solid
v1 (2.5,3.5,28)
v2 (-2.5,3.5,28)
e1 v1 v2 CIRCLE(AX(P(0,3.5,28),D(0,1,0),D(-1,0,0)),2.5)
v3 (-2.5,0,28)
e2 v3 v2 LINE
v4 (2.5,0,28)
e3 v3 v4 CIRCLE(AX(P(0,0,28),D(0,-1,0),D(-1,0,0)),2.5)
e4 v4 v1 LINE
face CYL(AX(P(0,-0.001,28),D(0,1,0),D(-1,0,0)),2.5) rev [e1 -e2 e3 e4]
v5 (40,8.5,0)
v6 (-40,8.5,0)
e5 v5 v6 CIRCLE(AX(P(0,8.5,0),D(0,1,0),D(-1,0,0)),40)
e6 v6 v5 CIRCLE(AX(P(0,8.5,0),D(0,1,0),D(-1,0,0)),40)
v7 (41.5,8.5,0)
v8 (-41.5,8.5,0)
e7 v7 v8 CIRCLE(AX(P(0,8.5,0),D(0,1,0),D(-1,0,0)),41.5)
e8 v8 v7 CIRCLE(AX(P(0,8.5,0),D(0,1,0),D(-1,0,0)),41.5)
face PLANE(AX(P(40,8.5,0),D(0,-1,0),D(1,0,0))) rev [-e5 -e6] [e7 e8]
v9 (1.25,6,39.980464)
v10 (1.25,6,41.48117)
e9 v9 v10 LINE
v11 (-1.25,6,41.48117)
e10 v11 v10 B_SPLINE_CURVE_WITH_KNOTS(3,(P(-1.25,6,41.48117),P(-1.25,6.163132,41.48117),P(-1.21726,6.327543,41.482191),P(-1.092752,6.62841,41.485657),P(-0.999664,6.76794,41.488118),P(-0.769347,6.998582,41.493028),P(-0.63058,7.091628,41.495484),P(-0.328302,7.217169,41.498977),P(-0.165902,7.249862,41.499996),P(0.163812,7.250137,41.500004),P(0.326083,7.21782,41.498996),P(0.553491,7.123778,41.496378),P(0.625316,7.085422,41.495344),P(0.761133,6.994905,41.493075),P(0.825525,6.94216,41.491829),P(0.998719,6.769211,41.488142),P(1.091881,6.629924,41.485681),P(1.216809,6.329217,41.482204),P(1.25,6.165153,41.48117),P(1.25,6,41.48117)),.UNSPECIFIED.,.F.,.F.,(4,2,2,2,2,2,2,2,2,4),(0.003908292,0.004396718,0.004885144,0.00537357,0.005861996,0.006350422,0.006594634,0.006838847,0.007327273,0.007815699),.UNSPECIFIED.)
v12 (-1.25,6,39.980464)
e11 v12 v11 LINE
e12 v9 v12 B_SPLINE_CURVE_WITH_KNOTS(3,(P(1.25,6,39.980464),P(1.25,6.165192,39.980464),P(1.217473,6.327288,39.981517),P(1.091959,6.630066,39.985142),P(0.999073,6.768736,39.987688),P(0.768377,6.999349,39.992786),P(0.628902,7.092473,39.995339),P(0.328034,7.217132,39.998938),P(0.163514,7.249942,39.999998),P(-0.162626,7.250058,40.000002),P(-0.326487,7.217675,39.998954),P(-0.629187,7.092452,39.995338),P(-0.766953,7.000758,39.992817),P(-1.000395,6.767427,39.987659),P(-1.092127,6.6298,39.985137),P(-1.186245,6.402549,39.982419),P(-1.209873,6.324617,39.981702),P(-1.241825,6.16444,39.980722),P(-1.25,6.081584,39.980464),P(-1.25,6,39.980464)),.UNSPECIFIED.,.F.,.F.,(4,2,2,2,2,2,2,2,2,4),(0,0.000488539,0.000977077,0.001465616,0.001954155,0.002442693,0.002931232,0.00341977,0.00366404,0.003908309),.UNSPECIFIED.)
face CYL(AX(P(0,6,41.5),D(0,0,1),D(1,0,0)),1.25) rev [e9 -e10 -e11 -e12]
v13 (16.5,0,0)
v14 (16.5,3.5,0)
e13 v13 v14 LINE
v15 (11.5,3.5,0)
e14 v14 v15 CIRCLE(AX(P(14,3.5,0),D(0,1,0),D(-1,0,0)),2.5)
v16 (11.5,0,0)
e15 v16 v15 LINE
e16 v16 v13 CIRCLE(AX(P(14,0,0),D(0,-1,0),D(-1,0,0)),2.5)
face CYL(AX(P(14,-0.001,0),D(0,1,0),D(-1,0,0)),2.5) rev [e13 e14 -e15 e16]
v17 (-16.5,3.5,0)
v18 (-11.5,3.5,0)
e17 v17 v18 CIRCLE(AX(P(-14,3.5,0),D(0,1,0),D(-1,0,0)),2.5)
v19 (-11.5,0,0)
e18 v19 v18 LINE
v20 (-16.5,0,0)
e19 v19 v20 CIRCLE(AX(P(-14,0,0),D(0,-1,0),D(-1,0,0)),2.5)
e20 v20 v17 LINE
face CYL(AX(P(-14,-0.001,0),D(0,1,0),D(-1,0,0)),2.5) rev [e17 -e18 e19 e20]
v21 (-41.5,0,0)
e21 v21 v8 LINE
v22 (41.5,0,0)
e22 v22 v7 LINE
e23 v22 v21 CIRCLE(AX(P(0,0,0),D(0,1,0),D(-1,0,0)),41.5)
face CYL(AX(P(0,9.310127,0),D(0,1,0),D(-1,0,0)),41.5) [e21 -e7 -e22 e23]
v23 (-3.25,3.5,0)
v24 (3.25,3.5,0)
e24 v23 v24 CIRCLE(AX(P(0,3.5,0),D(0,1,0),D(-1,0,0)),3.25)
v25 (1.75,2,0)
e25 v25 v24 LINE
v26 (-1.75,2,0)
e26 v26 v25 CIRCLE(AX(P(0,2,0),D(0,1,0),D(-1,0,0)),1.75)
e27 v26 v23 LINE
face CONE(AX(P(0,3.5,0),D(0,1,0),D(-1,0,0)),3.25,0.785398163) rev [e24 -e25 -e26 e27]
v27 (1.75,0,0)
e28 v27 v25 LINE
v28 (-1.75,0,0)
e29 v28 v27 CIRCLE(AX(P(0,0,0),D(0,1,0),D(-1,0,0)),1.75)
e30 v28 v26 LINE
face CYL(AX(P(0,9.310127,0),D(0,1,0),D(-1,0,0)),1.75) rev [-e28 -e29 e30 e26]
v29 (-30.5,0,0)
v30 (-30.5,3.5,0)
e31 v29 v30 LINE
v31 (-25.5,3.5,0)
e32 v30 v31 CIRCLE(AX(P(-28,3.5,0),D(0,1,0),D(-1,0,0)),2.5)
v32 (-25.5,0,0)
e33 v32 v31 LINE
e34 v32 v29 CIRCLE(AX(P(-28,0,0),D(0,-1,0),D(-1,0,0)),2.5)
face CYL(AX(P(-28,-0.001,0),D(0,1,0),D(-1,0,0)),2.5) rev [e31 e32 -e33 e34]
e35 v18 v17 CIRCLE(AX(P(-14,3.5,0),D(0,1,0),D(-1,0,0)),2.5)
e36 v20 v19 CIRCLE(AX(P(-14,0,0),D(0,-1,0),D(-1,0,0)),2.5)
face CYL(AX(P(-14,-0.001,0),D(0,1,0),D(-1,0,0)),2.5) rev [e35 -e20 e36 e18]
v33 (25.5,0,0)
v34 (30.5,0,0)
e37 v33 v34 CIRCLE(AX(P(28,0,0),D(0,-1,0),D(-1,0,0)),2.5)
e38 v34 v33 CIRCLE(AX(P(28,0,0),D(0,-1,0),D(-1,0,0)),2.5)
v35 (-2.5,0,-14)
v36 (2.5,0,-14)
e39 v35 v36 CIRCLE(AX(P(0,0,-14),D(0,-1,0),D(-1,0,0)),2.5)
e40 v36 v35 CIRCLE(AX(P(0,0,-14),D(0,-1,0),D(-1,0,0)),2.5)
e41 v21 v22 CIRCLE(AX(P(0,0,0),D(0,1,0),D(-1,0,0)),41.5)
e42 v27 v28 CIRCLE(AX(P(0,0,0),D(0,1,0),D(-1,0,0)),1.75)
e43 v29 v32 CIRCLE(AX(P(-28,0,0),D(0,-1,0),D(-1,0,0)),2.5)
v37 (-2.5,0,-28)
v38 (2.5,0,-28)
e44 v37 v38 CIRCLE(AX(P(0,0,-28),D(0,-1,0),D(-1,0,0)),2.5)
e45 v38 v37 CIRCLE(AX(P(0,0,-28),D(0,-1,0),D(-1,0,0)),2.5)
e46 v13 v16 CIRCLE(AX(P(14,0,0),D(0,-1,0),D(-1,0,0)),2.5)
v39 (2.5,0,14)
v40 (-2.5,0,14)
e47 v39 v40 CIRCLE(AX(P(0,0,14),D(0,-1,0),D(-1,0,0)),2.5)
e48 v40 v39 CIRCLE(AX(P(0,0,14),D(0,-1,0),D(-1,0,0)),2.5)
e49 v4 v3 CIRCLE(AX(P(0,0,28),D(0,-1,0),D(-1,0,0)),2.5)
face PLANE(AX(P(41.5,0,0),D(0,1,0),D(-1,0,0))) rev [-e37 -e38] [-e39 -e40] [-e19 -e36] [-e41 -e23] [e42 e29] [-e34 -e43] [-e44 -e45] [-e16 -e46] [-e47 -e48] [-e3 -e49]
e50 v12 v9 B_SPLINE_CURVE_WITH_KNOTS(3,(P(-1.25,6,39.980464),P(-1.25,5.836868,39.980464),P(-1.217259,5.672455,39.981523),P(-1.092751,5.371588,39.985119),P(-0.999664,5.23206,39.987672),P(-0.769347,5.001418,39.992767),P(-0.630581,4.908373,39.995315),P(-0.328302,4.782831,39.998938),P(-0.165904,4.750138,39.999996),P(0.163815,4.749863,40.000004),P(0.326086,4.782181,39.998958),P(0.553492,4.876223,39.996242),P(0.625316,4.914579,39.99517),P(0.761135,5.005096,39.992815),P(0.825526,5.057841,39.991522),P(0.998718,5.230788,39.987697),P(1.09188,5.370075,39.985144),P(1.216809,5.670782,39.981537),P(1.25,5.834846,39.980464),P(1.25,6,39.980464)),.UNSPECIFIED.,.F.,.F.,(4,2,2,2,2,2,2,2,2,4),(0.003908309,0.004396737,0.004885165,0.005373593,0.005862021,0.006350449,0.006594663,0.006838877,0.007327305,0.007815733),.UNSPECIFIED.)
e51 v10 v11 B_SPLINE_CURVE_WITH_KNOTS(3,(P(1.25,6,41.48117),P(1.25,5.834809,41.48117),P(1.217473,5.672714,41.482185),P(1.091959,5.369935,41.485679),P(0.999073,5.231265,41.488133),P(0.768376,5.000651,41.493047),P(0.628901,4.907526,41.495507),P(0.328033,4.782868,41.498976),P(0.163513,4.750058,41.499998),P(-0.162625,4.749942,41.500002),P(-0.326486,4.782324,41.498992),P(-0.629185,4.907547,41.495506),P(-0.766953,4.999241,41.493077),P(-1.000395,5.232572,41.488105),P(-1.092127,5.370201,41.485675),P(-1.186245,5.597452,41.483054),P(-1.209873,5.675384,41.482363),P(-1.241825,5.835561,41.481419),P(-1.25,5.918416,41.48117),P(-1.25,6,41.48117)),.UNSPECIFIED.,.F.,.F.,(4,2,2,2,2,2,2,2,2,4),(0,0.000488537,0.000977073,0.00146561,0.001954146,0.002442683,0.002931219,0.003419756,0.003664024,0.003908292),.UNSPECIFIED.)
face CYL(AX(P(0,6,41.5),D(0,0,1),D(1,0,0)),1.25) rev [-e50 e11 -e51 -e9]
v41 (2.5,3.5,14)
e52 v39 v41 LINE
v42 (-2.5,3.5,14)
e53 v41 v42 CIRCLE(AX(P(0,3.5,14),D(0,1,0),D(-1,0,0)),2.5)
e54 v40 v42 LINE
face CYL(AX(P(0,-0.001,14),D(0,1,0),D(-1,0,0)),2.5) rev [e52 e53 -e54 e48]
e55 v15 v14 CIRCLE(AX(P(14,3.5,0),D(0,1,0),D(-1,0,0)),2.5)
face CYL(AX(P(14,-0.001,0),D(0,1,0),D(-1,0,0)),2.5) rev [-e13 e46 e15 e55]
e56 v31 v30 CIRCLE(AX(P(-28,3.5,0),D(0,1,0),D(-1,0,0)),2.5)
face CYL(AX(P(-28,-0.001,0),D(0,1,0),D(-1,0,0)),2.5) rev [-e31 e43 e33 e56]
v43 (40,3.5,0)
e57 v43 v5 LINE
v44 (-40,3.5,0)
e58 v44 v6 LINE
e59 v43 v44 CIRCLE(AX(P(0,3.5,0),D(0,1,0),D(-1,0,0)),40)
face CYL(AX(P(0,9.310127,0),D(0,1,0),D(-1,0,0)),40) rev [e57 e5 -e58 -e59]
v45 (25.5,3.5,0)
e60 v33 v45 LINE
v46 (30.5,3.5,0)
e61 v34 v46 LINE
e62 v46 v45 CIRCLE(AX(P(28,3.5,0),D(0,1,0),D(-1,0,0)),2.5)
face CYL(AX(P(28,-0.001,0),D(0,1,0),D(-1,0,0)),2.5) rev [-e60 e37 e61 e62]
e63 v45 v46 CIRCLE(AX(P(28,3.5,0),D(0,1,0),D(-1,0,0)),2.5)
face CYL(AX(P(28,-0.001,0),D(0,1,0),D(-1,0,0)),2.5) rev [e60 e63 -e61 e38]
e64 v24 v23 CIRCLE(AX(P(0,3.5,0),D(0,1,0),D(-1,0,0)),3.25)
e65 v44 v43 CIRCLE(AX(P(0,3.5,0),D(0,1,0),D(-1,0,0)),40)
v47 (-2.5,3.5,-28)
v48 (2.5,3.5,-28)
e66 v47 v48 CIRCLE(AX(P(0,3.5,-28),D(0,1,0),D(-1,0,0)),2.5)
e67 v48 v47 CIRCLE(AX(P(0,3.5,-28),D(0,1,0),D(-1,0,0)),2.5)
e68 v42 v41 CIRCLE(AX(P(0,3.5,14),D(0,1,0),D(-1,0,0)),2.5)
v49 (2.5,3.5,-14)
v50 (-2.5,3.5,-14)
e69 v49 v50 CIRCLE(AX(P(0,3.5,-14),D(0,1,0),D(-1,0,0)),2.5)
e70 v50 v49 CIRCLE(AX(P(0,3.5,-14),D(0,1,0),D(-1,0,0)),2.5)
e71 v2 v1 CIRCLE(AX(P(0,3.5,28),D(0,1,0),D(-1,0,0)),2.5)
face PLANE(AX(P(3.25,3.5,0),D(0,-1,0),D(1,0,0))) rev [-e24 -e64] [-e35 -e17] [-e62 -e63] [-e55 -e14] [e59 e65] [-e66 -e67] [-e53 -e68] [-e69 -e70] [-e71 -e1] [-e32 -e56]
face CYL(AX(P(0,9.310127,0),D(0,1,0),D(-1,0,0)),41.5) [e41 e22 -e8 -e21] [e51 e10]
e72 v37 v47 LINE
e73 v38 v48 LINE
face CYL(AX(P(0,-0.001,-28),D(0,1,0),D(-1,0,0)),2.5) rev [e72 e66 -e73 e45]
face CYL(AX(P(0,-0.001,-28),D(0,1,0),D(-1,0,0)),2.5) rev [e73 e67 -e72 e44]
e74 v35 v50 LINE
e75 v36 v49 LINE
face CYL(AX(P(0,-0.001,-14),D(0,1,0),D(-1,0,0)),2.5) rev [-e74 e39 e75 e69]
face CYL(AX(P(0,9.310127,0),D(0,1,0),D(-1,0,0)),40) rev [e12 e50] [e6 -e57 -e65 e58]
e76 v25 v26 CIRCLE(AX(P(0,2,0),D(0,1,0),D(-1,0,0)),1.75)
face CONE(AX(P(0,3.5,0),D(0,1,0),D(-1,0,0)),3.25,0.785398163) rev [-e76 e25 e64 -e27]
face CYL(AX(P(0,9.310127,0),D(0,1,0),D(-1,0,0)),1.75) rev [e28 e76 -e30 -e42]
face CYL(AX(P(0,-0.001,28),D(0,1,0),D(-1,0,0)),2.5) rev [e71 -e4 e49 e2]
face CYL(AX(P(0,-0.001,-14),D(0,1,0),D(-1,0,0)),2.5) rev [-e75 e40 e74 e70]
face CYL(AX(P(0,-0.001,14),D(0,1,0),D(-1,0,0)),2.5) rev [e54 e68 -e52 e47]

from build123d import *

# Parameters (mm, degrees)
CUT_EXTRUDE1_REACH     = 60.902
SKETCH2_R              = 2.5
M3_TAPPED_HOLE1_REACH  = 94.991
M3_TAPPED_HOLE1_BORE_R = 1.25


with BuildPart() as part:
    # Sketch1 → Revolve1 (revolve)
    with BuildSketch(Plane.XY, mode=Mode.PRIVATE) as revolve1_sk:
        Polygon((1.75, 0), (1.75, 2), (3.25, 3.5), (40, 3.5), (40, 8.5), (41.5, 8.5), (41.5, 0), align=None)
    revolve(revolve1_sk.sketch.rotate(Axis((0, 9.310126582, 0), (0, -1, 0)), 180), axis=Axis((0, 9.310126582, 0), (0, -1, 0)))

    # Sketch2 → Cut-Extrude1 (cut, up to next)
    with BuildSketch(Plane(origin=(0, 3.5, 0), x_dir=(1, 0, 0), z_dir=(0, 1, 0)), mode=Mode.PRIVATE) as cut_extrude1_sk1:
        with Locations(Location((0, 14, 0), (0, 0, 180))):
            Circle(SKETCH2_R)
    cut_extrude1_tool1 = extrude(cut_extrude1_sk1.sketch, amount=-CUT_EXTRUDE1_REACH, mode=Mode.PRIVATE) & part.part
    # Sketch2 → Cut-Extrude1 (cut, up to next)
    with BuildSketch(Plane(origin=(0, 3.5, 0), x_dir=(1, 0, 0), z_dir=(0, 1, 0)), mode=Mode.PRIVATE) as cut_extrude1_sk2:
        with Locations(Location((14, 0, 0), (0, 0, 180))):
            Circle(SKETCH2_R)
    cut_extrude1_tool2 = extrude(cut_extrude1_sk2.sketch, amount=-CUT_EXTRUDE1_REACH, mode=Mode.PRIVATE) & part.part
    # Sketch2 → Cut-Extrude1 (cut, up to next)
    with BuildSketch(Plane(origin=(0, 3.5, 0), x_dir=(1, 0, 0), z_dir=(0, 1, 0)), mode=Mode.PRIVATE) as cut_extrude1_sk3:
        with Locations(Location((0, 28, 0), (0, 0, 180))):
            Circle(SKETCH2_R)
    cut_extrude1_tool3 = extrude(cut_extrude1_sk3.sketch, amount=-CUT_EXTRUDE1_REACH, mode=Mode.PRIVATE) & part.part
    # Sketch2 → Cut-Extrude1 (cut, up to next)
    with BuildSketch(Plane(origin=(0, 3.5, 0), x_dir=(1, 0, 0), z_dir=(0, 1, 0)), mode=Mode.PRIVATE) as cut_extrude1_sk4:
        with Locations(Location((28, 0, 0), (0, 0, 180))):
            Circle(SKETCH2_R)
    cut_extrude1_tool4 = extrude(cut_extrude1_sk4.sketch, amount=-CUT_EXTRUDE1_REACH, mode=Mode.PRIVATE) & part.part
    # Sketch2 → Cut-Extrude1 (cut, up to next)
    with BuildSketch(Plane(origin=(0, 3.5, 0), x_dir=(1, 0, 0), z_dir=(0, 1, 0)), mode=Mode.PRIVATE) as cut_extrude1_sk5:
        with Locations(Location((0, -14, 0), (0, 0, 180))):
            Circle(SKETCH2_R)
    cut_extrude1_tool5 = extrude(cut_extrude1_sk5.sketch, amount=-CUT_EXTRUDE1_REACH, mode=Mode.PRIVATE) & part.part
    # Sketch2 → Cut-Extrude1 (cut, up to next)
    with BuildSketch(Plane(origin=(0, 3.5, 0), x_dir=(1, 0, 0), z_dir=(0, 1, 0)), mode=Mode.PRIVATE) as cut_extrude1_sk6:
        with Locations(Location((0, -28, 0), (0, 0, 180))):
            Circle(SKETCH2_R)
    cut_extrude1_tool6 = extrude(cut_extrude1_sk6.sketch, amount=-CUT_EXTRUDE1_REACH, mode=Mode.PRIVATE) & part.part
    # Sketch2 → Cut-Extrude1 (cut, up to next)
    with BuildSketch(Plane(origin=(0, 3.5, 0), x_dir=(1, 0, 0), z_dir=(0, 1, 0)), mode=Mode.PRIVATE) as cut_extrude1_sk7:
        with Locations(Location((-14, 0, 0), (0, 0, 180))):
            Circle(SKETCH2_R)
    cut_extrude1_tool7 = extrude(cut_extrude1_sk7.sketch, amount=-CUT_EXTRUDE1_REACH, mode=Mode.PRIVATE) & part.part
    # Sketch2 → Cut-Extrude1 (cut, up to next)
    with BuildSketch(Plane(origin=(0, 3.5, 0), x_dir=(1, 0, 0), z_dir=(0, 1, 0)), mode=Mode.PRIVATE) as cut_extrude1_sk8:
        with Locations(Location((-28, 0, 0), (0, 0, 180))):
            Circle(SKETCH2_R)
    cut_extrude1_tool8 = extrude(cut_extrude1_sk8.sketch, amount=-CUT_EXTRUDE1_REACH, mode=Mode.PRIVATE) & part.part
    add(cut_extrude1_tool1.solids().sort_by_distance((0, 3.5, -14))[0], mode=Mode.SUBTRACT)
    add(cut_extrude1_tool2.solids().sort_by_distance((14, 3.5, 0))[0], mode=Mode.SUBTRACT)
    add(cut_extrude1_tool3.solids().sort_by_distance((0, 3.5, -28))[0], mode=Mode.SUBTRACT)
    add(cut_extrude1_tool4.solids().sort_by_distance((28, 3.5, 0))[0], mode=Mode.SUBTRACT)
    add(cut_extrude1_tool5.solids().sort_by_distance((0, 3.5, 14))[0], mode=Mode.SUBTRACT)
    add(cut_extrude1_tool6.solids().sort_by_distance((0, 3.5, 28))[0], mode=Mode.SUBTRACT)
    add(cut_extrude1_tool7.solids().sort_by_distance((-14, 3.5, 0))[0], mode=Mode.SUBTRACT)
    add(cut_extrude1_tool8.solids().sort_by_distance((-28, 3.5, 0))[0], mode=Mode.SUBTRACT)

    # M3 Tapped Hole1 bore (on position points) → M3 Tapped Hole1 (cut, up to next)
    with BuildSketch(Plane(origin=(0, 6, 41.5), x_dir=(1, 0, 0), z_dir=(0, 0, 1)), mode=Mode.PRIVATE) as m3_tapped_hole1_sk1:
        Circle(M3_TAPPED_HOLE1_BORE_R)
    m3_tapped_hole1_tool1 = extrude(m3_tapped_hole1_sk1.sketch, amount=-M3_TAPPED_HOLE1_REACH, mode=Mode.PRIVATE) & part.part
    add(m3_tapped_hole1_tool1.solids().sort_by_distance((0, 6, 41.5))[0], mode=Mode.SUBTRACT)


solid = part.part
